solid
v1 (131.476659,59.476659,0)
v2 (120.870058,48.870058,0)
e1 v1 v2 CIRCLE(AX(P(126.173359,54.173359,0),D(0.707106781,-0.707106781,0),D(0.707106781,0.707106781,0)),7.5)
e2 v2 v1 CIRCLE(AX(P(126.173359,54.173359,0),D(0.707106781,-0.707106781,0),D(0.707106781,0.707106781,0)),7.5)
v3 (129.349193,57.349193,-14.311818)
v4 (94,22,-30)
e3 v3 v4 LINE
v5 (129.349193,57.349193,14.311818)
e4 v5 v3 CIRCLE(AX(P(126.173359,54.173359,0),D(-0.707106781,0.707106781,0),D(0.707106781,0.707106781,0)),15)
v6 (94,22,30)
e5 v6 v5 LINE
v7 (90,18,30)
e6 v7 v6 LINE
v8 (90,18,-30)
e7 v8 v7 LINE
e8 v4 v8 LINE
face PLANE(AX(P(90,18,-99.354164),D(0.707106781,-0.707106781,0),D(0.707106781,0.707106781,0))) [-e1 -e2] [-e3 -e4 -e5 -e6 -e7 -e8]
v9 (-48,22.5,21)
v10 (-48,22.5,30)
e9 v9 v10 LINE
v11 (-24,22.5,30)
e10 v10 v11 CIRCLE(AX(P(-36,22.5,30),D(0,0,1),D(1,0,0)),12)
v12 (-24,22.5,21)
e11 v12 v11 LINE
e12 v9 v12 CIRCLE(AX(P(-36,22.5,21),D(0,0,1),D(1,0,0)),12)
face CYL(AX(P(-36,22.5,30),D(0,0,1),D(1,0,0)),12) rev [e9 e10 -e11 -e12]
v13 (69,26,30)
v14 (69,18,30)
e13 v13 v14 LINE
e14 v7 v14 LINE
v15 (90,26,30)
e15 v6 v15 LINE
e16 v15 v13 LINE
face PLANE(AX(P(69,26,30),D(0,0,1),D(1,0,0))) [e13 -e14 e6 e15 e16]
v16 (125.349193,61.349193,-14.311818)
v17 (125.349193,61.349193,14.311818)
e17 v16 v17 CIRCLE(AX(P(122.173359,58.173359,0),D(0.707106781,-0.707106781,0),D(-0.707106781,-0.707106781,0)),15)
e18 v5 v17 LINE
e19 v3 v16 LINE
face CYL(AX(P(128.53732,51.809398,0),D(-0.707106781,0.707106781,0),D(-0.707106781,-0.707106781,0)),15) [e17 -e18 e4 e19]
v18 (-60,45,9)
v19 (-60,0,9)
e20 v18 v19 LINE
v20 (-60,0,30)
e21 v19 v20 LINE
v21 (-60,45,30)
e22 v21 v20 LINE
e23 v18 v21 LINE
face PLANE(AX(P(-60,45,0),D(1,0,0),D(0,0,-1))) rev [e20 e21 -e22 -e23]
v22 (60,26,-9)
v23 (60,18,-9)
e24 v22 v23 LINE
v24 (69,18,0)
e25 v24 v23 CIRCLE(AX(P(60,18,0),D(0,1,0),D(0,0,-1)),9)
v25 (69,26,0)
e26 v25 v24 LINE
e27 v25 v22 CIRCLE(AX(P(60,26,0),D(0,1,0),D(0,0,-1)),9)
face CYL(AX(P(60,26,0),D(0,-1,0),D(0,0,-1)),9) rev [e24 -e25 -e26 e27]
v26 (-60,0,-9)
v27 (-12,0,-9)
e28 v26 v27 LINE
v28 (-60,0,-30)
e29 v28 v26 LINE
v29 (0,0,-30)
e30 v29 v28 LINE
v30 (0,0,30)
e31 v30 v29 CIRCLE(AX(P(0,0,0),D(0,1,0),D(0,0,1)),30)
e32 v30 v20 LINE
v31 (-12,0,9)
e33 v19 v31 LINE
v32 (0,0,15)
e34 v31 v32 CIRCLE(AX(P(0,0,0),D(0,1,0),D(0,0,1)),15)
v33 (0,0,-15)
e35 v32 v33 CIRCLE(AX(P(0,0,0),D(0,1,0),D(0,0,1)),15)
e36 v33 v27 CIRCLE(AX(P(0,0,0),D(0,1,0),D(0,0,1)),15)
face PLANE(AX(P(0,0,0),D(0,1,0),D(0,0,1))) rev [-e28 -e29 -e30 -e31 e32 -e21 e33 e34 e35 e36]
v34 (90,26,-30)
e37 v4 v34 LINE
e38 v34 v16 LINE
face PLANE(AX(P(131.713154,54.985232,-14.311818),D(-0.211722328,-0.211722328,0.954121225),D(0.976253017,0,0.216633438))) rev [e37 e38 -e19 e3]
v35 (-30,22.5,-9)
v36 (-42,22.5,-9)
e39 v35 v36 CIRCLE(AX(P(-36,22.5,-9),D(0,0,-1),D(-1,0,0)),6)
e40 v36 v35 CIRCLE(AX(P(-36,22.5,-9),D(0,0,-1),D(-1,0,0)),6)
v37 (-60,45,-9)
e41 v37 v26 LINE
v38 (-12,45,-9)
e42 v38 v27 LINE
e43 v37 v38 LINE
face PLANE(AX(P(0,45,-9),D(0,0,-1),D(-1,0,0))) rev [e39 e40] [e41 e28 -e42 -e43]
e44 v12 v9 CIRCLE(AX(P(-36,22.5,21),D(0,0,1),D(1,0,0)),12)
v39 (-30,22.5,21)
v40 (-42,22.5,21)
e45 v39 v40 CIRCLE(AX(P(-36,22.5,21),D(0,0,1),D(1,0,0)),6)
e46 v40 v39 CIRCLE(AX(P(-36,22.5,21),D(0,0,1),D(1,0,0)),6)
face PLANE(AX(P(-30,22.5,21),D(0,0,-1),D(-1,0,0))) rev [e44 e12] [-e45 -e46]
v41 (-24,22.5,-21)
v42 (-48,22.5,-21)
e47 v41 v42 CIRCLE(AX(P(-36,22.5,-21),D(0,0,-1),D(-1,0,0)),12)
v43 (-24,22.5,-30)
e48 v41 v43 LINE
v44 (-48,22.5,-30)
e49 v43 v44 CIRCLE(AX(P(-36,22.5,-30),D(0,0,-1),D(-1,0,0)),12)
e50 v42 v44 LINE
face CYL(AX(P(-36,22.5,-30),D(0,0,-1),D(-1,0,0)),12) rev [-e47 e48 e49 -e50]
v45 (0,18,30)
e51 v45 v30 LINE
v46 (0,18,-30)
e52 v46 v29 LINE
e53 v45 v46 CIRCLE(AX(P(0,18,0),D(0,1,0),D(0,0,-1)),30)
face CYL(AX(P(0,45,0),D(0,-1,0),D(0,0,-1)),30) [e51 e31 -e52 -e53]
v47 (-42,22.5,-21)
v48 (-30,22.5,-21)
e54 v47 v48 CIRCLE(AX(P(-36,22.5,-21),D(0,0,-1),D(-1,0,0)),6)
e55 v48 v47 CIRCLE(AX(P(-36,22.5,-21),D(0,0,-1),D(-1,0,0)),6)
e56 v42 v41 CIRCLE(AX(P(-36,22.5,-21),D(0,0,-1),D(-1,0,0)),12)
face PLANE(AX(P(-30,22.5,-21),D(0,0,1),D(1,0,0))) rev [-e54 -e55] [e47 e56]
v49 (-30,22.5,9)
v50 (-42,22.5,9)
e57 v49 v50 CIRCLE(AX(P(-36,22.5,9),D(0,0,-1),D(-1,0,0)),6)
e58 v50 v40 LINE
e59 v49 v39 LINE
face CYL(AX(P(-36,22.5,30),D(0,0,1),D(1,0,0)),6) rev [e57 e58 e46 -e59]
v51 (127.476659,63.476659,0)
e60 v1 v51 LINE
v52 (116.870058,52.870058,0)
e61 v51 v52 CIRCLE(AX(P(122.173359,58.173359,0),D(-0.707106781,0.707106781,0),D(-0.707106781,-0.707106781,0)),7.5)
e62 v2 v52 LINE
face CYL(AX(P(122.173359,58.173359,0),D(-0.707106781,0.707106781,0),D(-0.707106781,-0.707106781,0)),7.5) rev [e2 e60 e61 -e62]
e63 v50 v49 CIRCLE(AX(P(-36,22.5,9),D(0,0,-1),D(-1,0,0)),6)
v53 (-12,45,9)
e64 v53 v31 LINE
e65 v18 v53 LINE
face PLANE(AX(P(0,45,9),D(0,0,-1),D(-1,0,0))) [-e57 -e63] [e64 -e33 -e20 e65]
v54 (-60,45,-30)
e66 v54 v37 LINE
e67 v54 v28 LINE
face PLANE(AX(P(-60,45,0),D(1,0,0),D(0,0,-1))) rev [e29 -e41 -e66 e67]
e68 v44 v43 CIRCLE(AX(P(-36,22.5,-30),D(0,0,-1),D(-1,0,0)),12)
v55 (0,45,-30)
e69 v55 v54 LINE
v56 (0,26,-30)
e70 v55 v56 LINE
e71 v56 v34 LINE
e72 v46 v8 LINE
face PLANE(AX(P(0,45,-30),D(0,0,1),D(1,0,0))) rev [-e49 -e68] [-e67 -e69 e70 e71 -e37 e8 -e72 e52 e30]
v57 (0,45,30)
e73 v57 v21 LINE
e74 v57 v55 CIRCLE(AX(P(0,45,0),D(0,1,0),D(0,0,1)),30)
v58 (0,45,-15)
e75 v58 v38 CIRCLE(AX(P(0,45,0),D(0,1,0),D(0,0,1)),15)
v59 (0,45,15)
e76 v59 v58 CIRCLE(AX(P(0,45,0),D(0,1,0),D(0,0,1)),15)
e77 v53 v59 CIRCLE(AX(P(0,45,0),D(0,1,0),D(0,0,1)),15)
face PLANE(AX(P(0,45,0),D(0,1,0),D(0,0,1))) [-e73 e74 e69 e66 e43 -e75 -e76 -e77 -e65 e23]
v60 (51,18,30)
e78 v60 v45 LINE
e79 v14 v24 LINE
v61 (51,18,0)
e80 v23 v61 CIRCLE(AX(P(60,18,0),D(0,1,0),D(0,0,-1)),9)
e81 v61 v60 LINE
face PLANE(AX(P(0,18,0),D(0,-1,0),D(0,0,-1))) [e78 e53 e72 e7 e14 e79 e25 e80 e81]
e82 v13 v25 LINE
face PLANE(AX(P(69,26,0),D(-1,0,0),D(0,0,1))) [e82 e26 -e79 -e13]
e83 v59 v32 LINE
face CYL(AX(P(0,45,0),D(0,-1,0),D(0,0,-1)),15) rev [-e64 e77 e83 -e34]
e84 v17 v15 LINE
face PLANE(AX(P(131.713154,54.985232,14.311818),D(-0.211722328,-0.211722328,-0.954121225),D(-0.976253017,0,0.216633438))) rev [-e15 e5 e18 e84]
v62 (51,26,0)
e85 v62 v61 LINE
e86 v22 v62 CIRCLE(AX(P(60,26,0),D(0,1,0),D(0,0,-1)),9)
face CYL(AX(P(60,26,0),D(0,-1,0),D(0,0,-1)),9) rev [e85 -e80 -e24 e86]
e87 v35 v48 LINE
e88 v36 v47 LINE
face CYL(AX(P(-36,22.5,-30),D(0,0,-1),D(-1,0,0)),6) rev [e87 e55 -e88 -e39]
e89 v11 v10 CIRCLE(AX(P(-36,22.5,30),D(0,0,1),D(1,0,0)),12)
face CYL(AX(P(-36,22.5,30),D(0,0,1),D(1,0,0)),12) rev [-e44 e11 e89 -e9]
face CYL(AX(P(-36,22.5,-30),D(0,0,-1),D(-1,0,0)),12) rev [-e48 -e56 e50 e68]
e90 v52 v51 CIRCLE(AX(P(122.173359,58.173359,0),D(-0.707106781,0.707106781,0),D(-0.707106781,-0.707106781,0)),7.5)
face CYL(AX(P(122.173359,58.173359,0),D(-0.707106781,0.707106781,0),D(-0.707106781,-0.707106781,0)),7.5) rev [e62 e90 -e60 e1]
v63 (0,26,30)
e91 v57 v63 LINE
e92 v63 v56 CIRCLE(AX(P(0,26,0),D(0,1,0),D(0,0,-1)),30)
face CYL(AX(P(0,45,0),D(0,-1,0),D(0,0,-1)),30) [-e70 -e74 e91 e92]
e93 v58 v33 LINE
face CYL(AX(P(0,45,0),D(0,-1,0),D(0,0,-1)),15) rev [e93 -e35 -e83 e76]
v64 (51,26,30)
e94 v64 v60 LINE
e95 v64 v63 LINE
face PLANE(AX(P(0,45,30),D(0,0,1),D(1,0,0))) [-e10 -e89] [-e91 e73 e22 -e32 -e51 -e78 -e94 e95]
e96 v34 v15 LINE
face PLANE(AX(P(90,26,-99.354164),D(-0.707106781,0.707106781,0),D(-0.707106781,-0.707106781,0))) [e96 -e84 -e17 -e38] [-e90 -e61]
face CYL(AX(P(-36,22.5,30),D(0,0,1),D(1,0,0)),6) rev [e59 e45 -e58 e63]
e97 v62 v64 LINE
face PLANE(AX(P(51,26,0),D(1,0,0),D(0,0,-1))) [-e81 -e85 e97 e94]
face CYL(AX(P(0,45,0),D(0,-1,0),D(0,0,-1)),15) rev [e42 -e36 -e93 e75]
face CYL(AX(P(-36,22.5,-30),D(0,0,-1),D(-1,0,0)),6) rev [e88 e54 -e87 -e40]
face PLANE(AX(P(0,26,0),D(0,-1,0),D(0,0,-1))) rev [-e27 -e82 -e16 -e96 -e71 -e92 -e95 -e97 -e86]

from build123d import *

# Parameters (mm, degrees)
BASE_BLOCK_DEPTH                       = 45
SLOTTED_TAB_DEPTH                      = 8
ANGLED_LIP_DEPTH                       = 60
CLEVIS_SLOT_DEPTH                      = 9
CLEVIS_CROSS_HOLE_M14_15_D             = 15
COUNTERBORED_BOLT_HOLE_M10_D           = 12
COUNTERBORED_BOLT_HOLE_M10_DEPTH       = 21
COUNTERBORED_BOLT_HOLE_M10_CBORE_D     = 24
COUNTERBORED_BOLT_HOLE_M10_CBORE_DEPTH = 9


with BuildPart() as part:
    # Base Block Sketch → Base Block (new body)
    with BuildSketch(Plane(origin=(0, 0, 0), x_dir=(1, 0, 0), z_dir=(0, 1, 0))):
        with BuildLine():
            Line((-60, 30), (-60, 9))
            Line((-60, 9), (-12, 9))
            ThreePointArc((-12, 9), (15, 0), (-12, -9))
            Line((-12, -9), (-60, -9))
            Line((-60, -9), (-60, -30))
            Line((-60, -30), (0, -30))
            ThreePointArc((0, -30), (30, 0), (0, 30))
            Line((0, 30), (-60, 30))
        make_face()
    extrude(amount=BASE_BLOCK_DEPTH)

    # Slotted Tab Sketch → Slotted Tab (add)
    with BuildSketch(Plane(origin=(0, 18, 0), x_dir=(-1, 0, 0), z_dir=(0, -1, 0))):
        with BuildLine():
            Line((0, 30), (-51, 30))
            Line((-51, 30), (-90, 30))
            Line((-90, 30), (-90, -30))
            Line((-90, -30), (-69, -30))
            Line((-69, -30), (-69, 0))
            ThreePointArc((-69, 0), (-60, 9), (-51, 0))
            Line((-51, 0), (-51, -30))
            Line((-51, -30), (0, -30))
            ThreePointArc((0, -30), (-30, 0), (0, 30))
        make_face()
    extrude(amount=-SLOTTED_TAB_DEPTH)

    # Angled Lip Sketch → Angled Lip (add)
    with BuildSketch(Plane.XY.offset(30)):
        Polygon((90, 18), (137, 65), (133, 69), (90, 26), align=None)
    extrude(amount=-ANGLED_LIP_DEPTH)

    # Clevis Slot Sketch → Clevis Slot (cut)
    with BuildSketch(Plane(origin=(32, -32, 0), x_dir=(0, 0, 1), z_dir=(-0.7071067811865439, 0.7071067811865512, 0))):
        with BuildLine():
            Line((-14.311818372, 132.015695434), (-30, 82.024386618))
            Line((-30, 82.024386618), (-33.812783533, 82.024386618))
            Line((-33.812783533, 82.024386618), (-33.812783533, 155.319200691))
            Line((-33.812783533, 155.319200691), (36.02403622, 155.319200691))
            Line((36.02403622, 155.319200691), (36.02403622, 82.024386618))
            Line((36.02403622, 82.024386618), (30, 82.024386618))
            Line((30, 82.024386618), (14.311818372, 132.015695434))
            ThreePointArc((14.311818372, 132.015695434), (0, 142.524386618), (-14.311818372, 132.015695434))
        make_face()
    extrude(amount=-CLEVIS_SLOT_DEPTH, mode=Mode.SUBTRACT)

    # Clevis Cross Hole M14 Ø15 (through all)
    with Locations(Plane(origin=(32, -32, 0), x_dir=(0.7071067811865512, 0.7071067811865439, 0), z_dir=(-0.7071067811865439, 0.7071067811865512, 0))):
        with Locations((127.524386618, 0)):
            Hole(CLEVIS_CROSS_HOLE_M14_15_D / 2)

    # Counterbored Bolt Hole M10
    with Locations(Plane.XY.offset(30)):
        with Locations((-36, 22.5)):
            counterbored_bolt_hole_m10 = CounterBoreHole(COUNTERBORED_BOLT_HOLE_M10_D / 2, COUNTERBORED_BOLT_HOLE_M10_CBORE_D / 2, COUNTERBORED_BOLT_HOLE_M10_CBORE_DEPTH, depth=COUNTERBORED_BOLT_HOLE_M10_DEPTH)

    # Bolt Hole Mirror: Counterbored Bolt Hole M10 across plane
    add(counterbored_bolt_hole_m10.mirror(Plane.XY), mode=Mode.SUBTRACT)


solid = part.part
